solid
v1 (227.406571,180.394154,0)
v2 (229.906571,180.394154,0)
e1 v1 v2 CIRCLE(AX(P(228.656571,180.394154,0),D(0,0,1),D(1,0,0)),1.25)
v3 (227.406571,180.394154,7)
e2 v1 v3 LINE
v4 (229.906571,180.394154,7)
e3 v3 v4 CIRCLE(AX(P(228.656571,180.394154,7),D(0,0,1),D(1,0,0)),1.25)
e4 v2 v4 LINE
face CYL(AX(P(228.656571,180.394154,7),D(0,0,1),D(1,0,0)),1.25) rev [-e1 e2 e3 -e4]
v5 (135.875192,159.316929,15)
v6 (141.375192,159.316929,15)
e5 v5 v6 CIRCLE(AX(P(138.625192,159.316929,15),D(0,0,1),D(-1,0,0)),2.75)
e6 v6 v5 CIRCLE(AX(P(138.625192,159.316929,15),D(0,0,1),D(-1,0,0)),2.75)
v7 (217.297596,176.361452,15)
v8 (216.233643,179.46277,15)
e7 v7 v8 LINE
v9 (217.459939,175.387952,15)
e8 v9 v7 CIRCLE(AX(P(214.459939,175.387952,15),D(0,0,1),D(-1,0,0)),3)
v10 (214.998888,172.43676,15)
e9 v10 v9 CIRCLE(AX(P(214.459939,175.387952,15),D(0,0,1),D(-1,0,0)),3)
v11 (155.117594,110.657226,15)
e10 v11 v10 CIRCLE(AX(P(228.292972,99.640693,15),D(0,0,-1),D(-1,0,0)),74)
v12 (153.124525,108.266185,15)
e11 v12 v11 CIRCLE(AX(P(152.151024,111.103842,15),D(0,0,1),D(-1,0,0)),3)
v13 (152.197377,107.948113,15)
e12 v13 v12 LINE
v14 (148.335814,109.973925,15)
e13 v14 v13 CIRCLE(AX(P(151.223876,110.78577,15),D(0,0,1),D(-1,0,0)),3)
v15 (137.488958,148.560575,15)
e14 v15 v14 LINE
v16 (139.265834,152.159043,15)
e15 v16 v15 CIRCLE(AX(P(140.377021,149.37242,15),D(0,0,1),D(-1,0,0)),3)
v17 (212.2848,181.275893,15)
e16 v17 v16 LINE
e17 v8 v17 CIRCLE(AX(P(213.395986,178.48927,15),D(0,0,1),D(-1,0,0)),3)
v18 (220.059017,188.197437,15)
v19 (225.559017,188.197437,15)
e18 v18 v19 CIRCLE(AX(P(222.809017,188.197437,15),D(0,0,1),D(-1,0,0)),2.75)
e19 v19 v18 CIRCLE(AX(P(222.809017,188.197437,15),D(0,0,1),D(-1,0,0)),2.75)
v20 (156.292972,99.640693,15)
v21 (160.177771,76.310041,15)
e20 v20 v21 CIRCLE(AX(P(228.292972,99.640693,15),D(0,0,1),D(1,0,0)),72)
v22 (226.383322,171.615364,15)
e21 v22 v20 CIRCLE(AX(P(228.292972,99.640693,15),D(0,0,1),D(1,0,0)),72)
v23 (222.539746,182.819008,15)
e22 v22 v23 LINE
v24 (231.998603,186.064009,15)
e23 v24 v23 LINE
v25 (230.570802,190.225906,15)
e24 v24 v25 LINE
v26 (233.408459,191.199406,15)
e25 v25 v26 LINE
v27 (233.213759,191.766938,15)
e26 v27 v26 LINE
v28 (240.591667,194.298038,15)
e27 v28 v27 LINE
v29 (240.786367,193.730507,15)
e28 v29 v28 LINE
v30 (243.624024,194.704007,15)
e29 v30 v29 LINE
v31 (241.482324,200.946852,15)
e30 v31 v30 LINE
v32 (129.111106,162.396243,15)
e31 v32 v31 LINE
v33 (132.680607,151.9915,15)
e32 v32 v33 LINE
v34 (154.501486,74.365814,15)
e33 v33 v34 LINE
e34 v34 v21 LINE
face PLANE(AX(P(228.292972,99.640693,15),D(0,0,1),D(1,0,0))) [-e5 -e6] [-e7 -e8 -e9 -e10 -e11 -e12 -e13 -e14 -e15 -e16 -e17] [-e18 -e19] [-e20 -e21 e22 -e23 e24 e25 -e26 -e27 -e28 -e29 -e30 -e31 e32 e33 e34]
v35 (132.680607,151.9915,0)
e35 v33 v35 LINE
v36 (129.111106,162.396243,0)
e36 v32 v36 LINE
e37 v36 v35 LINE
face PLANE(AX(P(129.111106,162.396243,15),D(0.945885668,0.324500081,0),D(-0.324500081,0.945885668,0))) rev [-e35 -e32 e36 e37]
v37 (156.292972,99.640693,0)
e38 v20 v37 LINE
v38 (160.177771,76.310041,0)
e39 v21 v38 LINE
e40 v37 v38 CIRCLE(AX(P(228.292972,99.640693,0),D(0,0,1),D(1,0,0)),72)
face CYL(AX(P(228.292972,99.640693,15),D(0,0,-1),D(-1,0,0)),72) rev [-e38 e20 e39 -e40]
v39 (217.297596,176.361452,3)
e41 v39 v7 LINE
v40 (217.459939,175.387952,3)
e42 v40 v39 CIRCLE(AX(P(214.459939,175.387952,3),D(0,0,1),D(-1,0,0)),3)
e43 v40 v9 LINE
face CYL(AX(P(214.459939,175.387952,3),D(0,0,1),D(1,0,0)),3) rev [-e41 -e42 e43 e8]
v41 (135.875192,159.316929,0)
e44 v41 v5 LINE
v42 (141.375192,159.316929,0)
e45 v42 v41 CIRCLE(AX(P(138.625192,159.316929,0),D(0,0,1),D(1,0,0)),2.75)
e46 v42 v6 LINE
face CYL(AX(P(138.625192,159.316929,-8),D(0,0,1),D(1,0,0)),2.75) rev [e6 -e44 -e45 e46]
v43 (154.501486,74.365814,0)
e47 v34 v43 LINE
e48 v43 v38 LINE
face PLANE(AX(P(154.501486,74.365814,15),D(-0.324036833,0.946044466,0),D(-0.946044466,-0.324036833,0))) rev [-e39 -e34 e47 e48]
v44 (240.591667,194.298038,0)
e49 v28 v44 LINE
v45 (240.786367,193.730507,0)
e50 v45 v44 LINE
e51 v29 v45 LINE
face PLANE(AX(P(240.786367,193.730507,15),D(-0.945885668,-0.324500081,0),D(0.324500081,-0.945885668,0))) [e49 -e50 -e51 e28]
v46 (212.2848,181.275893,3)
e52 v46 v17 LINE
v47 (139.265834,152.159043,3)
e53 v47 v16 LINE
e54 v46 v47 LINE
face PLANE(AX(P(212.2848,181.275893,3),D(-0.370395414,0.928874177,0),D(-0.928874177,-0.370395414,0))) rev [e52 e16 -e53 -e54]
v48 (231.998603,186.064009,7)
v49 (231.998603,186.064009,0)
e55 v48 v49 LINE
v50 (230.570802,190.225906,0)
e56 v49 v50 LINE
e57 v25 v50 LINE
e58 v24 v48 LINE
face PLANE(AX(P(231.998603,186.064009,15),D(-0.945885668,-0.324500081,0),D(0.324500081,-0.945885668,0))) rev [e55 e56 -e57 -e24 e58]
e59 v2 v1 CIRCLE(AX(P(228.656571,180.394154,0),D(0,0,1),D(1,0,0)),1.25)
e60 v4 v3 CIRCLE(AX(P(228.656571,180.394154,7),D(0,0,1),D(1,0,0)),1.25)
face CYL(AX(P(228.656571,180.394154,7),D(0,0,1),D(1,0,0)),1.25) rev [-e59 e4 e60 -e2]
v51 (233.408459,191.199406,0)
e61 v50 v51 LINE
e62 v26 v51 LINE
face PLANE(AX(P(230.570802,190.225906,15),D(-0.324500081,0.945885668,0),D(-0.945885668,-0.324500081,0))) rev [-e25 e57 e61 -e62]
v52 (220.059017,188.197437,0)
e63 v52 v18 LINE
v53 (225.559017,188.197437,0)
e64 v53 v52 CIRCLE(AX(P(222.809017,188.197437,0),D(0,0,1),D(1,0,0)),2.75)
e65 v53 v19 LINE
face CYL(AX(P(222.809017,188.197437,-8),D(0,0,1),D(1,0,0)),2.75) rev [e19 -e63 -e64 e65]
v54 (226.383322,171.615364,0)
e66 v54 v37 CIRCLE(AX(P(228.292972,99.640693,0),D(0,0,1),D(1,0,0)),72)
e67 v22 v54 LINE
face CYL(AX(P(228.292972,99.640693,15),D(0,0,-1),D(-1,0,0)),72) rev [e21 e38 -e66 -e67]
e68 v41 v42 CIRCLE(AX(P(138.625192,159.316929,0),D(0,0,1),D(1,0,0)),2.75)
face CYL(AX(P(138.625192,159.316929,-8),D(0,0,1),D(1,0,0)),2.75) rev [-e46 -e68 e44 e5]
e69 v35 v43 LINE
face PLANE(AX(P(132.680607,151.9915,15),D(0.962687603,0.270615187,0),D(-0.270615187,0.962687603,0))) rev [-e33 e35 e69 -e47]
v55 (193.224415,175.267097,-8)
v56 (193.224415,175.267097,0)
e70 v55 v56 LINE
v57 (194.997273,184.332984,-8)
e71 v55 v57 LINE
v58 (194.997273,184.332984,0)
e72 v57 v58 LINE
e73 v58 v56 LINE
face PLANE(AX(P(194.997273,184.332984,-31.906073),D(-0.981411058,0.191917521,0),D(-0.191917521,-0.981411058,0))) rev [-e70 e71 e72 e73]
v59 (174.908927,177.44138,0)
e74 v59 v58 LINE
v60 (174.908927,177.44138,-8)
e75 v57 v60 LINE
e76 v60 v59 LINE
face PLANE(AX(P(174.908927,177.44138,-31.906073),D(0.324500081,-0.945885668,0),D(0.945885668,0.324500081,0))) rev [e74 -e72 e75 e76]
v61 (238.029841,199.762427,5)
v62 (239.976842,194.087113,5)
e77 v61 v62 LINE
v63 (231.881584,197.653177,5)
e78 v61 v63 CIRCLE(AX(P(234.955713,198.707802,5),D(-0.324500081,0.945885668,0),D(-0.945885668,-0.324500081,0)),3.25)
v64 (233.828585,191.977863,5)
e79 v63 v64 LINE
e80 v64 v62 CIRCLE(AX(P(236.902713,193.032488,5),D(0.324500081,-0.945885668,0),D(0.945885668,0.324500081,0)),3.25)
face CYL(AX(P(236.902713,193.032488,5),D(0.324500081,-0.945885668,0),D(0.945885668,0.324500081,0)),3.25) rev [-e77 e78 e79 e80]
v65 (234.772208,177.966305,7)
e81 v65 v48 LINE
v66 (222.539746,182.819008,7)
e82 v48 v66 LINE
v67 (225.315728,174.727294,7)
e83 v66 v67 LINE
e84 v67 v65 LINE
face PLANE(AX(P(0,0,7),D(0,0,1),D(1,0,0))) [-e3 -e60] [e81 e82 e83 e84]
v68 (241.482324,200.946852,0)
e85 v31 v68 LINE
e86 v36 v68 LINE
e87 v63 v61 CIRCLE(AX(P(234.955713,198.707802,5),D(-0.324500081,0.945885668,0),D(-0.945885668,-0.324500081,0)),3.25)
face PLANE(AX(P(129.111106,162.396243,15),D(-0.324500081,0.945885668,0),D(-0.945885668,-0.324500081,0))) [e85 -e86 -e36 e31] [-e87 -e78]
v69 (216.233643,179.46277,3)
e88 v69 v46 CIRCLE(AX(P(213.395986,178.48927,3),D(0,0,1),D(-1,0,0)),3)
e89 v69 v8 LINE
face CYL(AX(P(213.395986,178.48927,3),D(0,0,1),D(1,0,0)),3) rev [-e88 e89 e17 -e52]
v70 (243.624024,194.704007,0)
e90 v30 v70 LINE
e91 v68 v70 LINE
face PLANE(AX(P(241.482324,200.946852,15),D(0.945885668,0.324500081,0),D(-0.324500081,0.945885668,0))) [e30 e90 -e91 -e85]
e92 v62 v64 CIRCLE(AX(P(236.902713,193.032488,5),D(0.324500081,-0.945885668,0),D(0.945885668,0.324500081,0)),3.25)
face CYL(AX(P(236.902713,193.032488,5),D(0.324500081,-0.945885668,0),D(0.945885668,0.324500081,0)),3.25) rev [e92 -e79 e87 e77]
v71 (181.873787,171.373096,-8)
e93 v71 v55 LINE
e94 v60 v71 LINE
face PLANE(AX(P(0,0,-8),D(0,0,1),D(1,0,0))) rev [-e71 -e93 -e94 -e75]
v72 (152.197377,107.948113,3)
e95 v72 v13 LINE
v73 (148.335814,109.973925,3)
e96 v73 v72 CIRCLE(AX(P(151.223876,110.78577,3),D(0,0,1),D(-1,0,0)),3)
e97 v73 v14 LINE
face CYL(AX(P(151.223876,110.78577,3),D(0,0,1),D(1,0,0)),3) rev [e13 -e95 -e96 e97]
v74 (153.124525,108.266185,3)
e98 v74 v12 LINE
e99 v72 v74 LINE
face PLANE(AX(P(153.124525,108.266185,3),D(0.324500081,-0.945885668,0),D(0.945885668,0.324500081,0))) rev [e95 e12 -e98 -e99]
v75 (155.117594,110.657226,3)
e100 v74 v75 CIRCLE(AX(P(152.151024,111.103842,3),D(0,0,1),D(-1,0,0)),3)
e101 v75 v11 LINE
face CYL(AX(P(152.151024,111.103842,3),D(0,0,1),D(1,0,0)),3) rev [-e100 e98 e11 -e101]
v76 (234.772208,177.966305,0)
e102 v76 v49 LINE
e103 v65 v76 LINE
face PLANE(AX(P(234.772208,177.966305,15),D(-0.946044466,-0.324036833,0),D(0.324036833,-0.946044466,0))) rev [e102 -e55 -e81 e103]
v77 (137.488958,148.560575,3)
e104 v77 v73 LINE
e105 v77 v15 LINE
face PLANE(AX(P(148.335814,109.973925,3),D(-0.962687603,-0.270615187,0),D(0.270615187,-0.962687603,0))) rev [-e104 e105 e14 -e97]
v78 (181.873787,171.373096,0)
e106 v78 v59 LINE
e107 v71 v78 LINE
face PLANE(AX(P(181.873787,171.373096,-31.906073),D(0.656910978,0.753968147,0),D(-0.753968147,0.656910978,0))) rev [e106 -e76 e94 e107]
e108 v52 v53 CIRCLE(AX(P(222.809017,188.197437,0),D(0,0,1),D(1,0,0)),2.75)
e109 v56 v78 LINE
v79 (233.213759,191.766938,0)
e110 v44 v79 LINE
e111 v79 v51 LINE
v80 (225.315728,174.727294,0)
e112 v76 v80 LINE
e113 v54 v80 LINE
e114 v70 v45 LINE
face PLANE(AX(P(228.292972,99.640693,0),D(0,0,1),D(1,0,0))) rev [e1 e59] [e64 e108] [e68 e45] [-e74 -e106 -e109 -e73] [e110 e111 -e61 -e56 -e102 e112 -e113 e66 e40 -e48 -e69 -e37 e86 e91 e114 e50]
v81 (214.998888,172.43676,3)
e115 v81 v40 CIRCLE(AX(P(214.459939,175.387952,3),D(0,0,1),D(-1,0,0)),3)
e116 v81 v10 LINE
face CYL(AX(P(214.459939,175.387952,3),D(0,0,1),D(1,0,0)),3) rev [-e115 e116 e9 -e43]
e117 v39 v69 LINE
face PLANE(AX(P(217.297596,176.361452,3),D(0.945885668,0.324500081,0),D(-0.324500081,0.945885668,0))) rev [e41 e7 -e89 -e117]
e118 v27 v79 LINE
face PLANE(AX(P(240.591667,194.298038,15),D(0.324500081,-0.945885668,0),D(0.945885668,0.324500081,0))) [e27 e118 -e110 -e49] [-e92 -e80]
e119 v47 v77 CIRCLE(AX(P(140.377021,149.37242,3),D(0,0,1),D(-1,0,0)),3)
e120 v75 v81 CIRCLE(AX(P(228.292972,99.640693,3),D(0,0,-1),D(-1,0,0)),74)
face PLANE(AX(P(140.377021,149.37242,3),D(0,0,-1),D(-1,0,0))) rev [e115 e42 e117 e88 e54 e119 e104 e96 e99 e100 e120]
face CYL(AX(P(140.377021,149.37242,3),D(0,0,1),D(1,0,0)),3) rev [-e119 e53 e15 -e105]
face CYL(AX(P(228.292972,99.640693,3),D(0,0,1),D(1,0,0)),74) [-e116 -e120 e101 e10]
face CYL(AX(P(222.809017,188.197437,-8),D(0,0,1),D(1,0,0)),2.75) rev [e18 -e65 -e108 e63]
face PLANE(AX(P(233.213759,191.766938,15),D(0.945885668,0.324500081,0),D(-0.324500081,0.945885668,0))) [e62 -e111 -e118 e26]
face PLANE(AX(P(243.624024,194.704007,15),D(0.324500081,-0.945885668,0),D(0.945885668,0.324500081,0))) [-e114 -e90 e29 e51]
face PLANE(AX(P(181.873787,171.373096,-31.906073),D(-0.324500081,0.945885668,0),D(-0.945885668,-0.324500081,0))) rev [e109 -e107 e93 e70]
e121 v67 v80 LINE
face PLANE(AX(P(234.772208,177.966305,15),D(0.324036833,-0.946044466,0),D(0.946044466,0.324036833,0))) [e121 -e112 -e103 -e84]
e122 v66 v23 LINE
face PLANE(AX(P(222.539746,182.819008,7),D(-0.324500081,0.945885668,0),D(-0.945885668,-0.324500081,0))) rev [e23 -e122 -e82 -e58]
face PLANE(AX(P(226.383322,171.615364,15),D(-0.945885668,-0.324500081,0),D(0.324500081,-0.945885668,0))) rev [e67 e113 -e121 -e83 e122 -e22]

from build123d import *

# Parameters (mm, degrees)
EXTRUDE_1_DEPTH       = 15
EXTRUDE_2_DEPTH       = 8
CUT_EXTRUDE_1_DEPTH   = 12
CUT_EXTRUDE_2_DEPTH   = 8
SKETCH_5_R            = 0.5
CUT_EXTRUDE_3_DEPTH   = 317.640652423
SKETCH_6_R            = 2.75
CUT_EXTRUDE_4_DEPTH   = 317.640652423
HOLE_WIZARD_3_0_3_1_D = 6.5
HOLE_WIZARD_M3_1_D    = 2.5


with BuildPart() as part:
    # 草图1 → 凸台-拉伸1 (new body)
    with BuildSketch(Plane.XY):
        with BuildLine():
            Line((154.501486248, 74.365814355), (160.177770707, 76.310041404))
            ThreePointArc((160.177770707, 76.310041404), (169.160526734, 140.718106761), (226.383321785, 171.615364171))
            Line((226.383321785, 171.615364171), (225.315728088, 174.727294301))
            Line((225.315728088, 174.727294301), (234.77220836, 177.96630476))
            Line((234.77220836, 177.96630476), (231.998602564, 186.064008926))
            Line((231.998602564, 186.064008926), (230.57080221, 190.225905867))
            Line((230.57080221, 190.225905867), (233.408459215, 191.199406109))
            Line((233.408459215, 191.199406109), (233.213759167, 191.76693751))
            Line((233.213759167, 191.76693751), (240.591667381, 194.298038138))
            Line((240.591667381, 194.298038138), (240.786367429, 193.730506737))
            Line((240.786367429, 193.730506737), (243.624024434, 194.704006979))
            Line((243.624024434, 194.704006979), (241.482323903, 200.94685239))
            Line((241.482323903, 200.94685239), (129.111106493, 162.396242824))
            Line((129.111106493, 162.396242824), (132.680607379, 151.991500471))
            Line((132.680607379, 151.991500471), (154.501486248, 74.365814355))
        make_face()
    extrude(amount=EXTRUDE_1_DEPTH)

    # 草图2 → 凸台-拉伸2 (add)
    with BuildSketch(Plane(origin=(0, 0, 0), x_dir=(-1, 0, 0), z_dir=(0, 0, -1))):
        Polygon((-174.908927271, 177.441379972), (-194.997272817, 184.33298428), (-193.224414699, 175.267097261), (-181.873786677, 171.373096295), align=None)
    extrude(amount=EXTRUDE_2_DEPTH)

    # 草图3 → 切除-拉伸1 (cut)
    with BuildSketch(Plane.XY.offset(15)):
        with BuildLine():
            Line((148.33581351, 109.973924886), (137.488957816, 148.560574876))
            ThreePointArc((137.488957816, 148.560574876), (137.68708728, 150.700674405), (139.265834382, 152.159042969))
            Line((139.265834382, 152.159042969), (212.284799547, 181.275892717))
            ThreePointArc((212.284799547, 181.275892717), (214.647795853, 181.215617846), (216.233642795, 179.462770427))
            Line((216.233642795, 179.462770427), (217.297595906, 176.361452247))
            ThreePointArc((217.297595906, 176.361452247), (217.048600661, 173.871762608), (214.998888251, 172.436760111))
            ThreePointArc((214.998888251, 172.436760111), (175.157111586, 151.143900213), (155.117593814, 110.657226135))
            ThreePointArc((155.117593814, 110.657226135), (154.455434588, 109.182984766), (153.12452466, 108.266185323))
            Line((153.12452466, 108.266185323), (152.197376559, 107.948113442))
            ThreePointArc((152.197376559, 107.948113442), (149.830188599, 108.129149559), (148.33581351, 109.973924886))
        make_face()
    extrude(amount=-CUT_EXTRUDE_1_DEPTH, mode=Mode.SUBTRACT)

    # 草图4 → 切除-拉伸2 (cut)
    with BuildSketch(Plane.XY.offset(15)):
        Polygon((234.77220836, 177.96630476), (225.315728088, 174.727294301), (222.53974588, 182.819008121), (231.998602564, 186.064008926), align=None)
    extrude(amount=-CUT_EXTRUDE_2_DEPTH, mode=Mode.SUBTRACT)

    # 草图5 → 切除-拉伸3 (cut, through all)
    with BuildSketch(Plane.XY.offset(15)):
        with Locations((228.656571223, 180.394154027)):
            Circle(SKETCH_5_R)
    extrude(amount=-CUT_EXTRUDE_3_DEPTH, mode=Mode.SUBTRACT)

    # 草图6 → 切除-拉伸4 (cut, through all)
    with BuildSketch(Plane.XY.offset(15)):
        with Locations((138.625192324, 159.316929458)):
            Circle(SKETCH_6_R)
        with Locations((222.809016814, 188.197436624)):
            Circle(SKETCH_6_R)
    extrude(amount=-CUT_EXTRUDE_4_DEPTH, mode=Mode.SUBTRACT)

    # Ø3.0 (3) 直径孔1 (through all)
    with Locations(Plane(origin=(-34.303459783, 99.991195485, 0), x_dir=(-0.9458856684292948, -0.32450008052397505, 0), z_dir=(0.32450008052397505, -0.9458856684292948, 0))):
        with Locations((-286.72193914, -5)):
            Hole(HOLE_WIZARD_3_0_3_1_D / 2)

    # M3 螺纹孔1 (through all)
    with Locations(Plane.XY.offset(7)):
        with Locations((228.656571223, 180.394154027)):
            Hole(HOLE_WIZARD_M3_1_D / 2)


solid = part.part
